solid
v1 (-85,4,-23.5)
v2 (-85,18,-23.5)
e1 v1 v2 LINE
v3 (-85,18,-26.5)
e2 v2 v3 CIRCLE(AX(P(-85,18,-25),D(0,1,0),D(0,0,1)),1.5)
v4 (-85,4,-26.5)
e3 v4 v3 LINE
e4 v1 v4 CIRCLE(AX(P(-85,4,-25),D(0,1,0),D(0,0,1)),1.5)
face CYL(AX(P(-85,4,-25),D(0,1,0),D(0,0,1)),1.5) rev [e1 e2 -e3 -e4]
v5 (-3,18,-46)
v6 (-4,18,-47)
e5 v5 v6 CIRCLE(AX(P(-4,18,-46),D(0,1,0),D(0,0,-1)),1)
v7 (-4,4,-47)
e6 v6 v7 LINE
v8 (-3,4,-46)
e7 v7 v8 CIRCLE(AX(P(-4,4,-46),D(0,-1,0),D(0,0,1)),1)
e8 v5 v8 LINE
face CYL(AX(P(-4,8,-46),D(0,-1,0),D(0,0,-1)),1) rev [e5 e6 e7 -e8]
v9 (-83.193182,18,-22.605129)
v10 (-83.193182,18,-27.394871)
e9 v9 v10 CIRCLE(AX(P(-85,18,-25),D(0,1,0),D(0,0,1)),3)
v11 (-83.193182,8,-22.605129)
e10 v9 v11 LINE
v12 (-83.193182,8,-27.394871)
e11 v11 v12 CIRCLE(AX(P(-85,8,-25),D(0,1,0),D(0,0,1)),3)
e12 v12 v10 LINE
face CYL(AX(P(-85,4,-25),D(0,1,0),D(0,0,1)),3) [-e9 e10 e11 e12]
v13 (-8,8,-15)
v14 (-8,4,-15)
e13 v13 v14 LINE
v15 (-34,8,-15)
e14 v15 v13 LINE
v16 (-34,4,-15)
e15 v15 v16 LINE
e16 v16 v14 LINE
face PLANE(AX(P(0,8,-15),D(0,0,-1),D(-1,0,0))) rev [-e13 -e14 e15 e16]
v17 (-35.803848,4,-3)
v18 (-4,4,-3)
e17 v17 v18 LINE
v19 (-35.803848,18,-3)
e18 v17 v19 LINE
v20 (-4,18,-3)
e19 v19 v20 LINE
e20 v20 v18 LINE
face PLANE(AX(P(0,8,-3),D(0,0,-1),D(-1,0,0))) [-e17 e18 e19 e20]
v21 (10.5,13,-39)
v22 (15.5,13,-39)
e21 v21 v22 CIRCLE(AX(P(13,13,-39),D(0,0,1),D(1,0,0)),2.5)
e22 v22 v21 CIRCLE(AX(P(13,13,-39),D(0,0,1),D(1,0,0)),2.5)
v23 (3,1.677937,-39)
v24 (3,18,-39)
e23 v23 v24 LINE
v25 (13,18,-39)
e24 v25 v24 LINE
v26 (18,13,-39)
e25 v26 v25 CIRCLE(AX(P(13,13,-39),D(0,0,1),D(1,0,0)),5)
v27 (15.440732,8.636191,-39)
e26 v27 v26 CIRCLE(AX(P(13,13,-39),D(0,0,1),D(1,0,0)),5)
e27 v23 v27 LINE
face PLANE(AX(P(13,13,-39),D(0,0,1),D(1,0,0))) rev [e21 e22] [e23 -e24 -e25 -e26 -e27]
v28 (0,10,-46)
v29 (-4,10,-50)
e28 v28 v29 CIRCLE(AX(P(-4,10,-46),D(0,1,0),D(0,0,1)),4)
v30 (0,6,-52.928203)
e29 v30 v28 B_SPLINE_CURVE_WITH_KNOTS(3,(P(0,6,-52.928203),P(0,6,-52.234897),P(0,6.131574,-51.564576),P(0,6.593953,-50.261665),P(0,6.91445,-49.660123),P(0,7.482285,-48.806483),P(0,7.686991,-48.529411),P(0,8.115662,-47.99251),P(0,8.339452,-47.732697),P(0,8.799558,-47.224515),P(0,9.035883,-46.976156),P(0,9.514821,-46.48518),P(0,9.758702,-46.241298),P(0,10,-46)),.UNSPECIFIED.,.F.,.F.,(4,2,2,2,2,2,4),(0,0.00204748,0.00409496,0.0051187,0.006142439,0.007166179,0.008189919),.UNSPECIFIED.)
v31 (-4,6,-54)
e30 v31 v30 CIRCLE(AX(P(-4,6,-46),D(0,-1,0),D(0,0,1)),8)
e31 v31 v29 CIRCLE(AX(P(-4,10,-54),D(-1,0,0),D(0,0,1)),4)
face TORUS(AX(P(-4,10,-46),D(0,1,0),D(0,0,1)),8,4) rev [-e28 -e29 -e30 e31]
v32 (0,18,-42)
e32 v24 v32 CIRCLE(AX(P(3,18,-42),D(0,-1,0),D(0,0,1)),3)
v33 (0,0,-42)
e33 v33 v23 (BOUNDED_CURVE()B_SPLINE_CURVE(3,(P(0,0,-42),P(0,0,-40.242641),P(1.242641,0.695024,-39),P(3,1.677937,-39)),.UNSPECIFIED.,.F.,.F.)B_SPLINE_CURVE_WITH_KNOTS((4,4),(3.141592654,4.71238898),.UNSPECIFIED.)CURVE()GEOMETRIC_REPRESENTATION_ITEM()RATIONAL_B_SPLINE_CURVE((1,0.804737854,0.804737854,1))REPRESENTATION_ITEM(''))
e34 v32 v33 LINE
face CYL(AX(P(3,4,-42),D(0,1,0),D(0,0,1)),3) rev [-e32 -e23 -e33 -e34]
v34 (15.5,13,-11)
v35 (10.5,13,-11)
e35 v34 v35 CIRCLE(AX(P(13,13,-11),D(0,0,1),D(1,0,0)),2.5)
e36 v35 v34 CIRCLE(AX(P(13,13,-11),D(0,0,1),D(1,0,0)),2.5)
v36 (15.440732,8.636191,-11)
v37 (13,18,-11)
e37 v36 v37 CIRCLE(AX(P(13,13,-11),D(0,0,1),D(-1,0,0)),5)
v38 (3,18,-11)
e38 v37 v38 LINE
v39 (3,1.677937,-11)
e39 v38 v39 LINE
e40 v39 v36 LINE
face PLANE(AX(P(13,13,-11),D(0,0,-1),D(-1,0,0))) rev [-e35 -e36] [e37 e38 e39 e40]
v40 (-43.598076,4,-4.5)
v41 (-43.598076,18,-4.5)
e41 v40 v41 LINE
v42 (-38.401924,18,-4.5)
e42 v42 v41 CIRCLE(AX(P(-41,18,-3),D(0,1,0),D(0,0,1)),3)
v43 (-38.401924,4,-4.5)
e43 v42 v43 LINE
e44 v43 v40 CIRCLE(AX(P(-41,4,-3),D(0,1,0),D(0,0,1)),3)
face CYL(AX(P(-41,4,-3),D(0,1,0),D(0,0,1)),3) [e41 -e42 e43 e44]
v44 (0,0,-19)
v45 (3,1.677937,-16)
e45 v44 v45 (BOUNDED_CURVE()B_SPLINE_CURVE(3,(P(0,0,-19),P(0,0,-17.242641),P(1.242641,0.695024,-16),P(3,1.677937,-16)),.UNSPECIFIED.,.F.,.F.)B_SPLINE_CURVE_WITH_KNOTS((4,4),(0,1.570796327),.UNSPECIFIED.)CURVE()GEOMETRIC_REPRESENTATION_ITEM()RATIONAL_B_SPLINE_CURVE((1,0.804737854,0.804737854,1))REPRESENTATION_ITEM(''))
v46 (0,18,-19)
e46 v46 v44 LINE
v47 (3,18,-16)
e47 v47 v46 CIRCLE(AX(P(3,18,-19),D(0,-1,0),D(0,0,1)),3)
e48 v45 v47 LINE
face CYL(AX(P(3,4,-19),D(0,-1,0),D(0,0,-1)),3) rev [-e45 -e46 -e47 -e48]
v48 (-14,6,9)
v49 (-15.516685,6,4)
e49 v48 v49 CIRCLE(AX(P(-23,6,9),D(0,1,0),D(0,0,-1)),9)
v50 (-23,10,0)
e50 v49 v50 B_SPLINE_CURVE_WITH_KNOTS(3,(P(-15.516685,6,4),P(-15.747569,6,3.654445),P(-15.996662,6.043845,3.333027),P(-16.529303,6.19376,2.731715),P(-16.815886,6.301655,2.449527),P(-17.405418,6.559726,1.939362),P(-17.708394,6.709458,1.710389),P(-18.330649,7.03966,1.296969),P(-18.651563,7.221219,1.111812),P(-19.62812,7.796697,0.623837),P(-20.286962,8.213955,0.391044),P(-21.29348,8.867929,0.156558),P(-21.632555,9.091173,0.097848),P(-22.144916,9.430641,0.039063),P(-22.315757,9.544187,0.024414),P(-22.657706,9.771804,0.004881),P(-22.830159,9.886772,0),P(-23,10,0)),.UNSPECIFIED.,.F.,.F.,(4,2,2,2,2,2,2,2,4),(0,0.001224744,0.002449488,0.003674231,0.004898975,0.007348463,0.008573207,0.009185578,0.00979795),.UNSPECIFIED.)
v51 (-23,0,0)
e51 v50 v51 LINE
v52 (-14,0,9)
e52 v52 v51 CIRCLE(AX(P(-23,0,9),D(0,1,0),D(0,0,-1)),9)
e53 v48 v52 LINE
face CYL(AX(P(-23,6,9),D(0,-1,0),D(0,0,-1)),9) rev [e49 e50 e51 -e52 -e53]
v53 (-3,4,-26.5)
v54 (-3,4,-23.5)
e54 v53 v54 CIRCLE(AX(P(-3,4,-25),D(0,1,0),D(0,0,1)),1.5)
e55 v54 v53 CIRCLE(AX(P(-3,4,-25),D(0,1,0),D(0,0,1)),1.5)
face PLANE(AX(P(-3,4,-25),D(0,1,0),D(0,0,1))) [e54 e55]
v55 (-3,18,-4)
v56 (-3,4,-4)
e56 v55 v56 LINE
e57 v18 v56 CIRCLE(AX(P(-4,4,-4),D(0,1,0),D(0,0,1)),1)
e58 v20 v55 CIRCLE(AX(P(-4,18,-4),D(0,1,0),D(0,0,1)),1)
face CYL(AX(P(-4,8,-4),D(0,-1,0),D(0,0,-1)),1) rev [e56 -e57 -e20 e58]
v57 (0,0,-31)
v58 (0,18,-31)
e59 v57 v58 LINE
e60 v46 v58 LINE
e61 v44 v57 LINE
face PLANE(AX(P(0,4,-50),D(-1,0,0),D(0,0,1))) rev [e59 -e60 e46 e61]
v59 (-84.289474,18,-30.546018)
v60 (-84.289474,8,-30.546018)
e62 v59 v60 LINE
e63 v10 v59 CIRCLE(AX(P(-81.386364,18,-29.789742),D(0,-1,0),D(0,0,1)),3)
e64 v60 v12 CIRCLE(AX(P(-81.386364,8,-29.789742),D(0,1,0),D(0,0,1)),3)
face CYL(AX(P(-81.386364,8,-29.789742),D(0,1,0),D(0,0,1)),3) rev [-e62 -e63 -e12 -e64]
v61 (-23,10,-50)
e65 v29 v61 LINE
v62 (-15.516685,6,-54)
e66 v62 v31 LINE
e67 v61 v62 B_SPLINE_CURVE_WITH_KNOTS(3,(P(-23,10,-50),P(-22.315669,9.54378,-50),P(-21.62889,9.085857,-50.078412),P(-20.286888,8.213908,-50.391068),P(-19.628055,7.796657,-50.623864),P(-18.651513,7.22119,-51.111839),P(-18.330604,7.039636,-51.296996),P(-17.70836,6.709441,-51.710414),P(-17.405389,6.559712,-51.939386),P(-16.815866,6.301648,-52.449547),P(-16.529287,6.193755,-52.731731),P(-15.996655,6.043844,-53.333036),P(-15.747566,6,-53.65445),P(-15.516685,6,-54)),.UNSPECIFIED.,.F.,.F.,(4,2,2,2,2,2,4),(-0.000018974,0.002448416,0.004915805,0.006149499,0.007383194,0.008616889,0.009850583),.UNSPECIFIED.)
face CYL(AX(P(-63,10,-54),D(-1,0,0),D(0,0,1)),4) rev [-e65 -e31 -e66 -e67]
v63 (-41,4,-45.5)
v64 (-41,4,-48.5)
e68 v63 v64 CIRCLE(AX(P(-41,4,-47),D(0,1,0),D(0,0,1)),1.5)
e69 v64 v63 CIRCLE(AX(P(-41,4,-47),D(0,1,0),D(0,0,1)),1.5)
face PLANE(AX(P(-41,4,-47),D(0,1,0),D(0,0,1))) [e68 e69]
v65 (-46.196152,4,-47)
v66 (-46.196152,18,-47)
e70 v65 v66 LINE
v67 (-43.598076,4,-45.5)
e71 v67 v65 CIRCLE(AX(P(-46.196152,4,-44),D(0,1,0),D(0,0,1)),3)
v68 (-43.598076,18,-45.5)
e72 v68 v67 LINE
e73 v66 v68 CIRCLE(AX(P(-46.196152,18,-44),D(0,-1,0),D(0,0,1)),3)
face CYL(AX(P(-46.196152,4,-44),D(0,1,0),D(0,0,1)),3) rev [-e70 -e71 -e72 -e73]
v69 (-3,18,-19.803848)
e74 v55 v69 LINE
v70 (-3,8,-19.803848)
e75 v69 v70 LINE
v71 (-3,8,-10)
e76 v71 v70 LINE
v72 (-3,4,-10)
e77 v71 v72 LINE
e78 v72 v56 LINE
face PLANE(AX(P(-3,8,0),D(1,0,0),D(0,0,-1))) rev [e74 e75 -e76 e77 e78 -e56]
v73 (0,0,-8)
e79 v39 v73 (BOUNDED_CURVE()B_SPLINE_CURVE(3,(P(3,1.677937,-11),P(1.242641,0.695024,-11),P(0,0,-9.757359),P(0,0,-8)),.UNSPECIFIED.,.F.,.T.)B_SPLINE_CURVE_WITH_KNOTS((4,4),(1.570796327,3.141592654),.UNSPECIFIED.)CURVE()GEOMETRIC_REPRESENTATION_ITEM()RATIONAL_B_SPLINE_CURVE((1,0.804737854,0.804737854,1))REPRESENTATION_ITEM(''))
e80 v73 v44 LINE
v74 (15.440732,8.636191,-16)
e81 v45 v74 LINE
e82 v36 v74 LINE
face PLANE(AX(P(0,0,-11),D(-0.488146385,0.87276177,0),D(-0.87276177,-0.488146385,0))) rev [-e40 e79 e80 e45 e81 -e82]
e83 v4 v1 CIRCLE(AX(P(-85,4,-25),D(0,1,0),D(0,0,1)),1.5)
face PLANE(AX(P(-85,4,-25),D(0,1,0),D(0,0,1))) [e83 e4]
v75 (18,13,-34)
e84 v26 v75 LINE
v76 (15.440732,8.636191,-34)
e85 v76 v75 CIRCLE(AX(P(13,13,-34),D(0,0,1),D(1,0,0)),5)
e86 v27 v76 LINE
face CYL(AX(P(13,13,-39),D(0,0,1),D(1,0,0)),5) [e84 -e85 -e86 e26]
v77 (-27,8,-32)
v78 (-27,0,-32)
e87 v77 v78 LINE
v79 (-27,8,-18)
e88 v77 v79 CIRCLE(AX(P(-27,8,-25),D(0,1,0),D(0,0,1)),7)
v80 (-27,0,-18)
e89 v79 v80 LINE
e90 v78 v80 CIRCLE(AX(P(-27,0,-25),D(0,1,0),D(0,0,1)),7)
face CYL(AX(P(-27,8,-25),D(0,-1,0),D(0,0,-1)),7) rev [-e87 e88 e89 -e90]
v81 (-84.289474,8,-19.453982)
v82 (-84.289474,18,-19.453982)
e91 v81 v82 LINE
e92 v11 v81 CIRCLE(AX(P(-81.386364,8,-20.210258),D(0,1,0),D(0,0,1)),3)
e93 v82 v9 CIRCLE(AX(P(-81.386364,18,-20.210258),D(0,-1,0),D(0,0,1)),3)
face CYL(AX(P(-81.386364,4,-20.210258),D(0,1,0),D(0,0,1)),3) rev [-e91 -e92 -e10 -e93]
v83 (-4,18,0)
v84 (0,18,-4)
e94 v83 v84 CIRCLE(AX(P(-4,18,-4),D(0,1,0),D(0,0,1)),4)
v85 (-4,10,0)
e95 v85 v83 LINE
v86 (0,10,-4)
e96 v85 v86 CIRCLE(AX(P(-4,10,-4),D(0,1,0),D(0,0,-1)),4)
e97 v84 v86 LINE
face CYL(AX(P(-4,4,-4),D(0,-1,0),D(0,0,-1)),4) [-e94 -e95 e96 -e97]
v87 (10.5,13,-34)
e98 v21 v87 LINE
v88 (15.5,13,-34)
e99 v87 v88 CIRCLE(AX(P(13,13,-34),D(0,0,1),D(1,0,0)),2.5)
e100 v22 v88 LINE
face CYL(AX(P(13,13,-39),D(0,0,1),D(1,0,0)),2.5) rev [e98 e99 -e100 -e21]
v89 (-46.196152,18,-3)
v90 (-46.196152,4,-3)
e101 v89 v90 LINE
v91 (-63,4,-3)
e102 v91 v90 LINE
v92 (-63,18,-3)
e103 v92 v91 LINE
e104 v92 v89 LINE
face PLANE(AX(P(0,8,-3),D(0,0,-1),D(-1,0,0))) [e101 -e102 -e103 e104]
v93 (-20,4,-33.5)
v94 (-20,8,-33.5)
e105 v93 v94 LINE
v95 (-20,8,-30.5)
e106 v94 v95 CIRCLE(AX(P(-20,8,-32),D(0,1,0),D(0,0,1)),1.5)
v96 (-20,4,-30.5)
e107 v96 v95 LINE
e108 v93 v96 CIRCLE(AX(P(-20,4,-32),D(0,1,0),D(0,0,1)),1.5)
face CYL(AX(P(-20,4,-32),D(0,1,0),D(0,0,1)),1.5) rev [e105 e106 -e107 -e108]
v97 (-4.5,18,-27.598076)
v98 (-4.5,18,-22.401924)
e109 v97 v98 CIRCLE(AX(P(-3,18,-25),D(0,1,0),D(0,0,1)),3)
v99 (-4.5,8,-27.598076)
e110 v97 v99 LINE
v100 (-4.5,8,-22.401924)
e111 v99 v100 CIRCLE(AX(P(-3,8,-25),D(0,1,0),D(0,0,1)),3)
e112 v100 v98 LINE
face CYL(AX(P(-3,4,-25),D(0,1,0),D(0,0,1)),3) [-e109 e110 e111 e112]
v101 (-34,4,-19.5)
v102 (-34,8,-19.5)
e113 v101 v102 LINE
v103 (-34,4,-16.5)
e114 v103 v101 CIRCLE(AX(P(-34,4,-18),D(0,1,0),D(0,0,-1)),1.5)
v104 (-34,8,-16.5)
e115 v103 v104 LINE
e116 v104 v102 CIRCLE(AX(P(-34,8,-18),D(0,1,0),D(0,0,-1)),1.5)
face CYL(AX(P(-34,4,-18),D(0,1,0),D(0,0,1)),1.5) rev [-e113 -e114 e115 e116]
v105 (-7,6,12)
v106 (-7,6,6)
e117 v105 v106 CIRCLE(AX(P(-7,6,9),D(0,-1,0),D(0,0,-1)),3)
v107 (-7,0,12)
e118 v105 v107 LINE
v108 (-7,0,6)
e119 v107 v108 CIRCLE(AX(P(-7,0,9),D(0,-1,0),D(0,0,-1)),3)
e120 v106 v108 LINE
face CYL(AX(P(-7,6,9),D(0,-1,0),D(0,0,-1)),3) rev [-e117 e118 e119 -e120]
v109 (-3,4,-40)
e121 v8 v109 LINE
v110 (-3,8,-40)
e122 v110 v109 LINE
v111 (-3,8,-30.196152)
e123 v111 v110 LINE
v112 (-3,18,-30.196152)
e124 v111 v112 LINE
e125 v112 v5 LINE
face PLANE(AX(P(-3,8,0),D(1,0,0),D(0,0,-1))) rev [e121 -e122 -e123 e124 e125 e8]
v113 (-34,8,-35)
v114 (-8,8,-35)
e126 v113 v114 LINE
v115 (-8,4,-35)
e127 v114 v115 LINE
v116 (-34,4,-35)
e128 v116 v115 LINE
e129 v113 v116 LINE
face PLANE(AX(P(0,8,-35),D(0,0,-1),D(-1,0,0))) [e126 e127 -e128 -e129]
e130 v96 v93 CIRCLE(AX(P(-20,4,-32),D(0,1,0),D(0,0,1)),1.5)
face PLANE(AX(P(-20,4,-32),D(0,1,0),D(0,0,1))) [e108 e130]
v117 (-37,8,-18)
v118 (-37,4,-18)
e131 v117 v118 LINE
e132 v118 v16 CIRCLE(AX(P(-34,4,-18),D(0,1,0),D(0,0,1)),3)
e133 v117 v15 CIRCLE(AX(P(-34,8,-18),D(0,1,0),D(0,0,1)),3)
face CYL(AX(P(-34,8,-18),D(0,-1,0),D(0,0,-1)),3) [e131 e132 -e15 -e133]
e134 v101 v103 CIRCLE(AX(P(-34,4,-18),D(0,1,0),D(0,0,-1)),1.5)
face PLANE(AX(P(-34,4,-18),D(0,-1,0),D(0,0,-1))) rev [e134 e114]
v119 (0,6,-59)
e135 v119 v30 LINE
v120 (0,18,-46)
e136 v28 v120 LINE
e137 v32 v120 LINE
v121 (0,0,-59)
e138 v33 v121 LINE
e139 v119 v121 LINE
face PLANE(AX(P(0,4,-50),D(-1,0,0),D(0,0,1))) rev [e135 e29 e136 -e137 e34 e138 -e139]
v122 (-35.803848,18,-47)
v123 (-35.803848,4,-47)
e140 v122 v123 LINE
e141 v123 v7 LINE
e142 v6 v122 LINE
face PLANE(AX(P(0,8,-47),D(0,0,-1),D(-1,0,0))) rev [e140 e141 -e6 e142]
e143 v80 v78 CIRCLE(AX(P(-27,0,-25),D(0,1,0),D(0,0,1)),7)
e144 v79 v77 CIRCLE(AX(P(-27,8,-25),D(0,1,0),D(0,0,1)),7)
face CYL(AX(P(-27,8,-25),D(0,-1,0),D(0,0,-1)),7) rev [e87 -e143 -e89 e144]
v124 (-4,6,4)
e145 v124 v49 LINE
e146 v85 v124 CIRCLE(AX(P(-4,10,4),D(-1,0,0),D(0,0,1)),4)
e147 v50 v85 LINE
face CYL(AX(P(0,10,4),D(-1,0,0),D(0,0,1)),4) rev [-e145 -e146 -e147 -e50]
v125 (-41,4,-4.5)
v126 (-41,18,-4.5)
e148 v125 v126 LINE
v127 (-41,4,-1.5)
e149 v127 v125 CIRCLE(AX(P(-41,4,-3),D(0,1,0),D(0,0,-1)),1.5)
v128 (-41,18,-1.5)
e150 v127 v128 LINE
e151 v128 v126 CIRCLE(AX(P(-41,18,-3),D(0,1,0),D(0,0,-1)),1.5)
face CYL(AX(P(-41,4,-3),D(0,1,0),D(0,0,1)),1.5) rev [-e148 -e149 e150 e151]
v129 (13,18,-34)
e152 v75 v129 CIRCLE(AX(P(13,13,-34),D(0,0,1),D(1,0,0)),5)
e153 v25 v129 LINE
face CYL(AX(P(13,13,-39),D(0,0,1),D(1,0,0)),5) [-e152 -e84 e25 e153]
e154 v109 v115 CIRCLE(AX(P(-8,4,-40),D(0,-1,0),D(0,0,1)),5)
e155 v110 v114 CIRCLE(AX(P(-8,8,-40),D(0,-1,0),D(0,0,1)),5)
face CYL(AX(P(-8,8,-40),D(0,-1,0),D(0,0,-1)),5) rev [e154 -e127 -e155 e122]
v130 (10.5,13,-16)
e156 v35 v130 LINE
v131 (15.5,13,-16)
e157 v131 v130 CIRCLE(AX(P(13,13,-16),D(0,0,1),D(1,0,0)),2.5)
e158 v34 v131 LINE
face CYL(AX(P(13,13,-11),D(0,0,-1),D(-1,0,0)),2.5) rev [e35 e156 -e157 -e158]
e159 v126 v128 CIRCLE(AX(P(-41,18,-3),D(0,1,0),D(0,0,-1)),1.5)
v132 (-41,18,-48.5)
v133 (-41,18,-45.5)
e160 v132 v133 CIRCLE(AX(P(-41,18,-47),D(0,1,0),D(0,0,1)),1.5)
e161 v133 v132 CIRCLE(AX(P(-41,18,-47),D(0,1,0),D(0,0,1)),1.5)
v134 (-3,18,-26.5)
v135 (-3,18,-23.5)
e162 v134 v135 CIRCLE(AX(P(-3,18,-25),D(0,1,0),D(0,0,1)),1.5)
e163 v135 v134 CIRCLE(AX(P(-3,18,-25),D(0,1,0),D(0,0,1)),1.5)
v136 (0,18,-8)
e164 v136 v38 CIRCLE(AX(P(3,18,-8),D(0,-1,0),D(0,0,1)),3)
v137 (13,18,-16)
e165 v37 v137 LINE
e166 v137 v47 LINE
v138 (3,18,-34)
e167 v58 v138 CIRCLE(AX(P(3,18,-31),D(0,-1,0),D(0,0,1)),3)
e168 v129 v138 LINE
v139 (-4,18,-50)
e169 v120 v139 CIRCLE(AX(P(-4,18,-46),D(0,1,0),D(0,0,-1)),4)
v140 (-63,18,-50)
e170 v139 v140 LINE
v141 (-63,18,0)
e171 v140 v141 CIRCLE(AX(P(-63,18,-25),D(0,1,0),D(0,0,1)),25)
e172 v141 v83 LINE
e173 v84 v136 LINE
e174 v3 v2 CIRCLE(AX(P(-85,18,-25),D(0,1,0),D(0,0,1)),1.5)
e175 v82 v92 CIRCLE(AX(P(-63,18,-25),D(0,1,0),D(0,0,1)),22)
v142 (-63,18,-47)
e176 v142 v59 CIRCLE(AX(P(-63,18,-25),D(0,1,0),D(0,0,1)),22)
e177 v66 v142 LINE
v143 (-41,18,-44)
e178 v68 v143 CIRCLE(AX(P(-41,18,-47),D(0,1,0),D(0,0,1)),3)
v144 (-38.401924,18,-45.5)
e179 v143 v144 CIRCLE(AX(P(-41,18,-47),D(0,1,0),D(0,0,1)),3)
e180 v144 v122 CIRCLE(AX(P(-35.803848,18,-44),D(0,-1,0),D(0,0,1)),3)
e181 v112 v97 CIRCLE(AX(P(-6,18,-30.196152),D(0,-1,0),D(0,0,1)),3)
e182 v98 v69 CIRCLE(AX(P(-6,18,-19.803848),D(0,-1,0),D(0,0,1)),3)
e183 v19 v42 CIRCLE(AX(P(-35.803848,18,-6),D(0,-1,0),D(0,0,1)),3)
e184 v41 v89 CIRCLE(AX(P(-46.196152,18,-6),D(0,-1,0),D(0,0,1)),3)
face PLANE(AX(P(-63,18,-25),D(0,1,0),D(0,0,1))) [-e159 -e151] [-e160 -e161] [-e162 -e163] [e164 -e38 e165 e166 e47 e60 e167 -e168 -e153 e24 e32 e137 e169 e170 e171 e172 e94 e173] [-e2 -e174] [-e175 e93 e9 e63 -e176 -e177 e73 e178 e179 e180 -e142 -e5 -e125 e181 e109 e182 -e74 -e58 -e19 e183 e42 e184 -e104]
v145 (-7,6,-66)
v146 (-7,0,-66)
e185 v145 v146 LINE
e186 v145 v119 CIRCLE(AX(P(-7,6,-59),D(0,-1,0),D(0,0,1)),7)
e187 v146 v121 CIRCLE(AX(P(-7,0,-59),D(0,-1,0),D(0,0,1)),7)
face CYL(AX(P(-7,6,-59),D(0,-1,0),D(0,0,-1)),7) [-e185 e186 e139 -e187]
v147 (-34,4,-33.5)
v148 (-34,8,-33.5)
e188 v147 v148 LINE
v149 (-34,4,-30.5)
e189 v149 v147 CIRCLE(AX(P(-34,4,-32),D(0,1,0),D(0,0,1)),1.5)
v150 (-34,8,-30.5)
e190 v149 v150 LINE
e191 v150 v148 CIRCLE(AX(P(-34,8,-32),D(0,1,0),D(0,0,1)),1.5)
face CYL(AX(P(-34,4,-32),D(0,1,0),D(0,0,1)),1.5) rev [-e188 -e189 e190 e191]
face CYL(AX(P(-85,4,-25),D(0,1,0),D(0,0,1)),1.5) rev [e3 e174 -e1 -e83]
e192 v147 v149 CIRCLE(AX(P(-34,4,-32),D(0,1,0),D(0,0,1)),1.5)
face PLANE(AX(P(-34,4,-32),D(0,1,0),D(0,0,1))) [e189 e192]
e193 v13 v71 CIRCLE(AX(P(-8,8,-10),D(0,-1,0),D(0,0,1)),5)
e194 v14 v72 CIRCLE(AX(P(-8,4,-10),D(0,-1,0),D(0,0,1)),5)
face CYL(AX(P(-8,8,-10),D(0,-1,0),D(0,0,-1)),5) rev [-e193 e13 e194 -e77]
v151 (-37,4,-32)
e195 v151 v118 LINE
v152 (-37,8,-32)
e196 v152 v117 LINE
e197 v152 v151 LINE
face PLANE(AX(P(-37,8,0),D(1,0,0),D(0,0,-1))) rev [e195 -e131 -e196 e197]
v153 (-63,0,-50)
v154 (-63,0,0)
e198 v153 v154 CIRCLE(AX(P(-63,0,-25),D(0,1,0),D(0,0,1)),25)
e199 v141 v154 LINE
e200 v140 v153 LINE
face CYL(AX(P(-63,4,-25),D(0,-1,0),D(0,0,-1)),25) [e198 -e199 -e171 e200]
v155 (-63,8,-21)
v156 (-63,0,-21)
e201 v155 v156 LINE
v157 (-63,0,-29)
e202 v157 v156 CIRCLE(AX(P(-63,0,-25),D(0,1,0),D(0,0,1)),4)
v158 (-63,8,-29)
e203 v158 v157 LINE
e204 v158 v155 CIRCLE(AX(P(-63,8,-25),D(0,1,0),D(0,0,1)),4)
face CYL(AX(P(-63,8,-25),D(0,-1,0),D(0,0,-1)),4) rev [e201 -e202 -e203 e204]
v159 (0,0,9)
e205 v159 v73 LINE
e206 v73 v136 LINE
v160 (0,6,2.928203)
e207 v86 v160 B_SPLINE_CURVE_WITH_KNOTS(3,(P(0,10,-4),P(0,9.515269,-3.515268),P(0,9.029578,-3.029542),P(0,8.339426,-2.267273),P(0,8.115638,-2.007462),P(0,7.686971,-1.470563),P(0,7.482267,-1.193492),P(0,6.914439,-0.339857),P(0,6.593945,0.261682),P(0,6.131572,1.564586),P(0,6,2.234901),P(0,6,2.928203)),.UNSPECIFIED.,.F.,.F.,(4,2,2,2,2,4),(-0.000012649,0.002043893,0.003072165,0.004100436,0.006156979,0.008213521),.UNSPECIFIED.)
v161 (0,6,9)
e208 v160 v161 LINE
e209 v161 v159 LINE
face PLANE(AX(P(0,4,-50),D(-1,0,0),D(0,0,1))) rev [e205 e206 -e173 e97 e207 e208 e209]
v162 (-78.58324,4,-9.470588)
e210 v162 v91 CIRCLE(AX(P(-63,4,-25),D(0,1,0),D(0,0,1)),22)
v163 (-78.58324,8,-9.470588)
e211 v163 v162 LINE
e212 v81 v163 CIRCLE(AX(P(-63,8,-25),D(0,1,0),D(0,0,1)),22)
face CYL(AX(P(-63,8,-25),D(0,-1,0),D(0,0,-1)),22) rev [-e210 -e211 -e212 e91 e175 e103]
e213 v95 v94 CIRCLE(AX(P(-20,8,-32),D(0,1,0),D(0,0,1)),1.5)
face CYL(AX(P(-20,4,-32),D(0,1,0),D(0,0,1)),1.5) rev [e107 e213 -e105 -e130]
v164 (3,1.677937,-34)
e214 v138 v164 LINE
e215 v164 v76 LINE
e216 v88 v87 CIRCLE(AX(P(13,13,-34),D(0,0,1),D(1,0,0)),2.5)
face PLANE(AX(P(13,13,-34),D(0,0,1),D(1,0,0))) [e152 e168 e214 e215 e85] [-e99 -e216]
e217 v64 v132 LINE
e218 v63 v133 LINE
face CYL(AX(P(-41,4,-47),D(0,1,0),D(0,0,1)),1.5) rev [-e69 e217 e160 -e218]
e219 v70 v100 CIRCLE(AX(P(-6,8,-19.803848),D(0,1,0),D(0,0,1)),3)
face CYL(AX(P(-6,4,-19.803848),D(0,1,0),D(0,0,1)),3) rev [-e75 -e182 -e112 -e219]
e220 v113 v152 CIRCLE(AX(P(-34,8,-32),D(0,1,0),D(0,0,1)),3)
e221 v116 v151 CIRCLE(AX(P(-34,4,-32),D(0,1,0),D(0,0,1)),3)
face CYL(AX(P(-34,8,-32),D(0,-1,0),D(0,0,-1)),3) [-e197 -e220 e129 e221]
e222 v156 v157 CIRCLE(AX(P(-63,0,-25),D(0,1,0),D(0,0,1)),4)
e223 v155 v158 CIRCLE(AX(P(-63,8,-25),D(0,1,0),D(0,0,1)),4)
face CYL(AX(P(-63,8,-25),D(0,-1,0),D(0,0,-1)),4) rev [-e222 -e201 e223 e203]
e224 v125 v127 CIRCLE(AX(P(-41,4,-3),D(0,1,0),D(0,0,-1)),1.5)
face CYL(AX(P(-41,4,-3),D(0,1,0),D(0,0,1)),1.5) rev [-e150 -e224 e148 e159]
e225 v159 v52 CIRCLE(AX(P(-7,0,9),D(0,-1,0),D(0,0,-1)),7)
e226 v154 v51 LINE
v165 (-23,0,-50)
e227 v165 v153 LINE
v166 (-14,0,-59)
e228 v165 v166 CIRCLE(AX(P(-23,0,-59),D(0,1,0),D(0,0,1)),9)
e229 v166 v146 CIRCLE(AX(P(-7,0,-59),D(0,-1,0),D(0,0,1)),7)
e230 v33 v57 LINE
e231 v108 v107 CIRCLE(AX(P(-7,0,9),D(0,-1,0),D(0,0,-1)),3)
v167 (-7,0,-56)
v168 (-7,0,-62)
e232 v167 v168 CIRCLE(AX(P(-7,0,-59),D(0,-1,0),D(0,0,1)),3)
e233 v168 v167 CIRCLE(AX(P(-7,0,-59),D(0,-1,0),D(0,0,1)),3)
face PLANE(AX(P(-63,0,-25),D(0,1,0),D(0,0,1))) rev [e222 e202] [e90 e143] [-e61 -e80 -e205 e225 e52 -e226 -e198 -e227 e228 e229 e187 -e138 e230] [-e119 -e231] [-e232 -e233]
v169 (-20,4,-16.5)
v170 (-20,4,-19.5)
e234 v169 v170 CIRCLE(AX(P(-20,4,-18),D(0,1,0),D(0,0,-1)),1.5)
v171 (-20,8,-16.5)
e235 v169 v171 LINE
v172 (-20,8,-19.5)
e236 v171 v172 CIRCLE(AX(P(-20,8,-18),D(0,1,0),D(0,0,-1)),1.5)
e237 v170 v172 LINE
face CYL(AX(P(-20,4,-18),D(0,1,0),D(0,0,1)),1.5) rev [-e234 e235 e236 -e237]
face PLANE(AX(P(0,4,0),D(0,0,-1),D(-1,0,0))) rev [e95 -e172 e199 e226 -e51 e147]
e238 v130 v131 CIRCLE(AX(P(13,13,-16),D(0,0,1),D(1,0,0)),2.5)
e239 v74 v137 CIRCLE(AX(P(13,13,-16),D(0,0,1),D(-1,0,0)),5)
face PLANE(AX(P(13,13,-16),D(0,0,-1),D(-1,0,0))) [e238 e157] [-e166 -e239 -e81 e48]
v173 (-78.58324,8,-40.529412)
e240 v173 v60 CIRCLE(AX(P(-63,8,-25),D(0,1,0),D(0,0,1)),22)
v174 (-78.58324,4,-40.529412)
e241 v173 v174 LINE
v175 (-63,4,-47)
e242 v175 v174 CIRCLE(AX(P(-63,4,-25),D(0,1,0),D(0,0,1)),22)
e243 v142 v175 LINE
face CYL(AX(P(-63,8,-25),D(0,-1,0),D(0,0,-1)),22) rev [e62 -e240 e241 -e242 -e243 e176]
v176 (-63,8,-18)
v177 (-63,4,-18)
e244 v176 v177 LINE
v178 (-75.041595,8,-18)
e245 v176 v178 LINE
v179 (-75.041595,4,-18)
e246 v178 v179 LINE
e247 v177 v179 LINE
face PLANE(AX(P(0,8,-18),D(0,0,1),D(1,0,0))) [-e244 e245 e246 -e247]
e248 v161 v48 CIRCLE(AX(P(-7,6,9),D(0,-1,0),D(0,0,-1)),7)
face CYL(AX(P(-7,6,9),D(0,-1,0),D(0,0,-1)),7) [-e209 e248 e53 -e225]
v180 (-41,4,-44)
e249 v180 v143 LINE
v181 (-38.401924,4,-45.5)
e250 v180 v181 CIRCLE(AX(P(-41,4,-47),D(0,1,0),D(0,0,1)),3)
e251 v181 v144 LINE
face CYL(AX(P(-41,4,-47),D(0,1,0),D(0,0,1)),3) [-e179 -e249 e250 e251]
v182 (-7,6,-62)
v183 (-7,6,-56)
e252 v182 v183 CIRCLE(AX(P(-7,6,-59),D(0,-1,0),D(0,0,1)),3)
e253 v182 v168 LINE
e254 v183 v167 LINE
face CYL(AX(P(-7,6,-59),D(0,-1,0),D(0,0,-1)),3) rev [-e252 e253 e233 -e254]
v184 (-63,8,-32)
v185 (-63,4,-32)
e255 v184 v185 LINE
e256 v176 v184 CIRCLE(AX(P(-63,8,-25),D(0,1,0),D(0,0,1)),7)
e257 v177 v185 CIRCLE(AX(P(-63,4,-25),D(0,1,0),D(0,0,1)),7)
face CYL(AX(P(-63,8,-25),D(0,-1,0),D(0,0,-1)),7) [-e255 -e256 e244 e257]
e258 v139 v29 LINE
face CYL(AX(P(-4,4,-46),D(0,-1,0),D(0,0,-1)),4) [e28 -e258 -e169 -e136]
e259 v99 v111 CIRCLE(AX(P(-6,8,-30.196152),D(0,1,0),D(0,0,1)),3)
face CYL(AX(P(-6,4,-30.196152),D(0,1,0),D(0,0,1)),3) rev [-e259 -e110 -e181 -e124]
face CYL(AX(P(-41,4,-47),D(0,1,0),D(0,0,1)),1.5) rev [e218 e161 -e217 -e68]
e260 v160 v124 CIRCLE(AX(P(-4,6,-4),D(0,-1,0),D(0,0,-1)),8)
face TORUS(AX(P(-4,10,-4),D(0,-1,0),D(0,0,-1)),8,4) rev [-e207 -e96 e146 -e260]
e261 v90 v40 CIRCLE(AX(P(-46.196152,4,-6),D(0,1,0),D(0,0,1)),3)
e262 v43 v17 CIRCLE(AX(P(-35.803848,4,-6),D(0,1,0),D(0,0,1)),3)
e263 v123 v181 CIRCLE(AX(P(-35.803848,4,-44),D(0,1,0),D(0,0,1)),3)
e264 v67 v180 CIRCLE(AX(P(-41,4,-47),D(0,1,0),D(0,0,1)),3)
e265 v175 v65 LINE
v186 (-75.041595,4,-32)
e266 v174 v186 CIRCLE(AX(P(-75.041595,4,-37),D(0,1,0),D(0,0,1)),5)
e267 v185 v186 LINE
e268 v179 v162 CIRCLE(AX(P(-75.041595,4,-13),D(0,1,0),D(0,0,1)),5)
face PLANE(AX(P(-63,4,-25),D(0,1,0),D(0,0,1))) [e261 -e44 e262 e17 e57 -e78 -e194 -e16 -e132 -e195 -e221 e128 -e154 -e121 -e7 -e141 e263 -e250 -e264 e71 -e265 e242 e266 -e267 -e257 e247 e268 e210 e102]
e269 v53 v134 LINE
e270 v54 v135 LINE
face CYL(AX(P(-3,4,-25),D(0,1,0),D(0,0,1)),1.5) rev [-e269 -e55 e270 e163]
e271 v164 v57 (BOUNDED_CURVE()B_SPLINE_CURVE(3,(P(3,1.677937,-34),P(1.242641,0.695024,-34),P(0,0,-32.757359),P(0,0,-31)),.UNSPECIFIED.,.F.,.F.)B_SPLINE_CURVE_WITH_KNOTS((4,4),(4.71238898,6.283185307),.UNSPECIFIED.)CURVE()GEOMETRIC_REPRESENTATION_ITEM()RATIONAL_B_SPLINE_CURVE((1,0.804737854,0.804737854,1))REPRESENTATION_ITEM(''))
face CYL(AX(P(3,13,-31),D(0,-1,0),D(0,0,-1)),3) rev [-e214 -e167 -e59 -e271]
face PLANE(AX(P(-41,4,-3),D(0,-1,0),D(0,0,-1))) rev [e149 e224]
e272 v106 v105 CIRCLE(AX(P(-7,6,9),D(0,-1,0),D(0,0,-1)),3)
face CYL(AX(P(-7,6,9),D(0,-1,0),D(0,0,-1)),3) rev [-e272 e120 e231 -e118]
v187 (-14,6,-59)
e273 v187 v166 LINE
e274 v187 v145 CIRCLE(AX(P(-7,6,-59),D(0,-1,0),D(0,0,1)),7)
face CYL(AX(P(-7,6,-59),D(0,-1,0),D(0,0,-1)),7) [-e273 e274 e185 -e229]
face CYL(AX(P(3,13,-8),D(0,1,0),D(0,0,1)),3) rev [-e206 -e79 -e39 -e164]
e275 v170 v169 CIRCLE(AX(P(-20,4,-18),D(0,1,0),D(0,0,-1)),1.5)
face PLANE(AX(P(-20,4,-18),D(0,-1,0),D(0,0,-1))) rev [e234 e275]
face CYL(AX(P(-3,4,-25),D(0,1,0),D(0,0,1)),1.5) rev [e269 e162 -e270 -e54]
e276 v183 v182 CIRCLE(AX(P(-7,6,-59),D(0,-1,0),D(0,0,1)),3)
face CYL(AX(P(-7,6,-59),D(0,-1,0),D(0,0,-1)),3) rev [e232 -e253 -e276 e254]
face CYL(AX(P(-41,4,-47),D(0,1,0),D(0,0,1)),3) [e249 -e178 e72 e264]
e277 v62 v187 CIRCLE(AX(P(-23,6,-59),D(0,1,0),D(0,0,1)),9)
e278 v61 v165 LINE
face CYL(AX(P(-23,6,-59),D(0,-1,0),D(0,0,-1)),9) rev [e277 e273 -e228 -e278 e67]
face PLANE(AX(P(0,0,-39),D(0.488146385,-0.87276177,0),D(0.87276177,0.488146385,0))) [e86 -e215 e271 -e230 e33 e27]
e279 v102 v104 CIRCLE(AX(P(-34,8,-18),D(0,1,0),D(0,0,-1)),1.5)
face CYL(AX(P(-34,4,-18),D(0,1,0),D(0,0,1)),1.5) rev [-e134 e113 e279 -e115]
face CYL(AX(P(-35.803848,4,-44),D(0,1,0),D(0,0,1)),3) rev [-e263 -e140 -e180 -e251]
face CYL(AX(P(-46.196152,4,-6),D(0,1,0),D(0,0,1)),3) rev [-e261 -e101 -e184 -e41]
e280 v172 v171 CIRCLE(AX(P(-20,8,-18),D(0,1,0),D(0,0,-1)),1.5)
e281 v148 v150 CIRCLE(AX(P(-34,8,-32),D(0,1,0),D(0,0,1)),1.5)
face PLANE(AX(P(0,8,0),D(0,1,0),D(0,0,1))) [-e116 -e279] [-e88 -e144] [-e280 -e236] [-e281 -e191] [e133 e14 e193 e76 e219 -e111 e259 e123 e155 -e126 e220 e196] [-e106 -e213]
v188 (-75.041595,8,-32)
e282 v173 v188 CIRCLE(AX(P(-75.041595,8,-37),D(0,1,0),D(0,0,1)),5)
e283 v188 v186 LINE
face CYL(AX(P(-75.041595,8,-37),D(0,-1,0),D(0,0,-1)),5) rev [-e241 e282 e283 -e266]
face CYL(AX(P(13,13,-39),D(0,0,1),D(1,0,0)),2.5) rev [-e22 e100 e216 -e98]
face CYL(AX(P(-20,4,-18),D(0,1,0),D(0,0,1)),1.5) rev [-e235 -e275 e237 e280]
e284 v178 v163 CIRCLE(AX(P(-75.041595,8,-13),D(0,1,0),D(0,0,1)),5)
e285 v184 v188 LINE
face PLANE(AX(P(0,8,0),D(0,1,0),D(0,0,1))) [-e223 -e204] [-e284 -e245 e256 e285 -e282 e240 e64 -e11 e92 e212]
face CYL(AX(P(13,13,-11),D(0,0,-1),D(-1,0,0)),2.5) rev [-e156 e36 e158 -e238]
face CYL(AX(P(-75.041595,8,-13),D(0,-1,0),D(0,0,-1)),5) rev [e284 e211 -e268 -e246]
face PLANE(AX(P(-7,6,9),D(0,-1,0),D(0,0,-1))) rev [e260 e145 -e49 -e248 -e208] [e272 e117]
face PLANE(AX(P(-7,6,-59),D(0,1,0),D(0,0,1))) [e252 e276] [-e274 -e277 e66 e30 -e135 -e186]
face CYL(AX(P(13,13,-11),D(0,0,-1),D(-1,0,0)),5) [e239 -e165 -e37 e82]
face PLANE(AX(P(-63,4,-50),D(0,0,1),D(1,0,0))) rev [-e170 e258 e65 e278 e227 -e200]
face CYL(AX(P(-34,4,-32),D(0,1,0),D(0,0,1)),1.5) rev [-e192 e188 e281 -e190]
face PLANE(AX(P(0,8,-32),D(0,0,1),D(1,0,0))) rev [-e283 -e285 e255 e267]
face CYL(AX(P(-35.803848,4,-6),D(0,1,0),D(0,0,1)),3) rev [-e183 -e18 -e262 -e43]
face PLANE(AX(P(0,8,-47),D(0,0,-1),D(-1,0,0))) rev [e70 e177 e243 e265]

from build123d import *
from build123d.topology import SkipClean

# Parameters (mm, degrees)
BASE_PLATE_4MM_DEPTH       = 4
BASE_PLATE_FILLET_R4_R     = 4
HOUSING_START              = 4
HOUSING_WALL_SKETCH_R      = 7
HOUSING_WALL_SKETCH_R_2    = 4
HOUSING_WALLS_DEPTH        = 4
WALL_START                 = 10
WALL_RIM_10MM_DEPTH        = 10
BEARING_BOSS_14MM_DEPTH    = 14
BOSS_POCKET_SKETCH_R       = 1.5
BOSS_POCKET_CUT_DEPTH      = 14
WALL_SLOT_SKETCH_R         = 4
WALL_SLOT_SKETCH_R_2       = 7
WALL_SLOT_CUT_DEPTH        = 14
BEARING_BOSS_FILLET_R3_A_R = 3
BEARING_BOSS_FILLET_R3_B_R = 3
WALL_NOTCH_SKETCH_R        = 1.5
WALL_NOTCH_CUT_DEPTH       = 4
MOUNTING_START             = -6
MOUNTING_EAR_SKETCH_R      = 3
MOUNTING_EARS_6MM_DEPTH    = 6
SIDE_LUG_SKETCH_R          = 2.5
SIDE_LUG_5MM_DEPTH         = 5
SIDE_LUG_FILLET_R3_R       = 3
CLEVIS_START               = 5
CLEVIS_LUG_SKETCH_R        = 2.5
CLEVIS_LUG_5MM_DEPTH       = 5
CLEVIS_LUG_FILLET_R3_R     = 3
MOUNTING_EAR_FILLET_R4_A_R = 4
MOUNTING_EAR_FILLET_R4_B_R = 4


with BuildPart() as part:
    # Base Plate Sketch → Base Plate 4mm (new body)
    with BuildSketch(Plane(origin=(0, 0, 0), x_dir=(1, 0, 0), z_dir=(0, 1, 0))):
        with BuildLine():
            Line((0, 0), (-63, 0))
            ThreePointArc((-63, 0), (-88, 25), (-63, 50))
            Line((-63, 50), (0, 50))
            Line((0, 50), (0, 0))
        make_face()
    extrude(amount=BASE_PLATE_4MM_DEPTH)

    # Base Plate Fillet R4
    base_plate_fillet_r4_edges = [part.edges().sort_by_distance(p)[0] for p in [
        (0, 2, 0),
        (0, 2, -50),
    ]]
    fillet(base_plate_fillet_r4_edges, radius=BASE_PLATE_FILLET_R4_R)

    # Housing Wall Sketch → Housing Walls (add)
    # profile 1 of 4: a face of its own
    with BuildSketch(Plane(origin=(0, 4, 0), x_dir=(1, 0, 0), z_dir=(0, 1, 0)).offset(HOUSING_START)):
        with BuildLine():
            ThreePointArc((-4, 0), (-1.171572875, 1.171572875), (0, 4))
            Line((0, 4), (0, 46))
            ThreePointArc((0, 46), (-1.171572875, 48.828427125), (-4, 50))
            Line((-4, 50), (-63, 50))
            ThreePointArc((-63, 50), (-88, 25), (-63, 0))
            Line((-63, 0), (-4, 0))
        make_face()
        with BuildLine():
            Line((-63, 47), (-4, 47))
            ThreePointArc((-4, 47), (-3.292893219, 46.707106781), (-3, 46))
            Line((-3, 46), (-3, 4))
            ThreePointArc((-3, 4), (-3.292893219, 3.292893219), (-4, 3))
            Line((-4, 3), (-63, 3))
            ThreePointArc((-63, 3), (-85, 25), (-63, 47))
        make_face(mode=Mode.SUBTRACT)
    # profile 2 of 4: a face of its own
    with BuildSketch(Plane(origin=(0, 4, 0), x_dir=(1, 0, 0), z_dir=(0, 1, 0)).offset(HOUSING_START)):
        with BuildLine():
            ThreePointArc((-8, 15), (-4.464466094, 13.535533906), (-3, 10))
            Line((-3, 10), (-3, 40))
            ThreePointArc((-3, 40), (-4.464466094, 36.464466094), (-8, 35))
            Line((-8, 35), (-34, 35))
            ThreePointArc((-34, 35), (-36.121320344, 34.121320344), (-37, 32))
            Line((-37, 32), (-37, 18))
            ThreePointArc((-37, 18), (-36.121320344, 15.878679656), (-34, 15))
            Line((-34, 15), (-8, 15))
        make_face()
        with Locations(Location((-27, 25, 0), (0, 0, 270))):
            Circle(HOUSING_WALL_SKETCH_R, mode=Mode.SUBTRACT)
    # profile 3 of 4: a face of its own
    with BuildSketch(Plane(origin=(0, 4, 0), x_dir=(1, 0, 0), z_dir=(0, 1, 0)).offset(HOUSING_START)):
        with Locations((-63, 25)):
            Circle(HOUSING_WALL_SKETCH_R)
        with Locations(Location((-63, 25, 0), (0, 0, 270))):
            Circle(HOUSING_WALL_SKETCH_R_2, mode=Mode.SUBTRACT)
    # profile 4 of 4: a face of its own
    with BuildSketch(Plane(origin=(0, 4, 0), x_dir=(1, 0, 0), z_dir=(0, 1, 0)).offset(HOUSING_START)):
        with BuildLine():
            ThreePointArc((-78.583240043, 40.529411765), (-85, 25), (-78.583240043, 9.470588235))
            ThreePointArc((-78.583240043, 9.470588235), (-79.659335305, 14.917412472), (-75.041594579, 18))
            Line((-75.041594579, 18), (-63, 18))
            ThreePointArc((-63, 18), (-70, 25), (-63, 32))
            Line((-63, 32), (-75.041594579, 32))
            ThreePointArc((-75.041594579, 32), (-79.659335305, 35.082587528), (-78.583240043, 40.529411765))
        make_face()
    extrude(amount=-HOUSING_WALLS_DEPTH)

    # Wall Rim Sketch → Wall Rim 10mm (add)
    with SkipClean():  # the faces are left unmerged after this step: merging them gives an invalid solid
        with BuildSketch(Plane(origin=(0, 8, 0), x_dir=(1, 0, 0), z_dir=(0, 1, 0)).offset(WALL_START)):
            with BuildLine():
                Line((-63, 50), (-4, 50))
                ThreePointArc((-4, 50), (-1.171572875, 48.828427125), (0, 46))
                Line((0, 46), (0, 4))
                ThreePointArc((0, 4), (-1.171572875, 1.171572875), (-4, 0))
                Line((-4, 0), (-63, 0))
                ThreePointArc((-63, 0), (-88, 25), (-63, 50))
            make_face()
            with BuildLine():
                Line((-63, 3), (-4, 3))
                ThreePointArc((-4, 3), (-3.292893219, 3.292893219), (-3, 4))
                Line((-3, 4), (-3, 46))
                ThreePointArc((-3, 46), (-3.292893219, 46.707106781), (-4, 47))
                Line((-4, 47), (-63, 47))
                ThreePointArc((-63, 47), (-85, 25), (-63, 3))
            make_face(mode=Mode.SUBTRACT)
        extrude(amount=-WALL_RIM_10MM_DEPTH)

    # Bearing Boss Sketch → Bearing Boss 14mm (add)
    with BuildSketch(Plane(origin=(0, 18, 0), x_dir=(1, 0, 0), z_dir=(0, 1, 0))):
        with BuildLine():
            ThreePointArc((-84.795454545, 22.006981264), (-82, 25), (-84.795454545, 27.993018736))
            ThreePointArc((-84.795454545, 27.993018736), (-85, 25), (-84.795454545, 22.006981264))
        make_face()
        with BuildLine():
            ThreePointArc((-38, 3), (-41, 6), (-44, 3))
            Line((-44, 3), (-38, 3))
        make_face()
        with BuildLine():
            Line((-3, 22), (-3, 28))
            ThreePointArc((-3, 28), (-6, 25), (-3, 22))
        make_face()
        with BuildLine():
            Line((-38, 47), (-44, 47))
            ThreePointArc((-44, 47), (-41, 44), (-38, 47))
        make_face()
    extrude(amount=-BEARING_BOSS_14MM_DEPTH)

    # Boss Pocket Sketch → Boss Pocket Cut (cut)
    with BuildSketch(Plane(origin=(0, 18, 0), x_dir=(1, 0, 0), z_dir=(0, 1, 0))):
        with Locations(Location((-85, 25, 0), (0, 0, 270))):
            Circle(BOSS_POCKET_SKETCH_R)
        with Locations(Location((-41, 3, 0), (0, 0, 90))):
            Circle(BOSS_POCKET_SKETCH_R)
        with Locations(Location((-41, 47, 0), (0, 0, 270))):
            Circle(BOSS_POCKET_SKETCH_R)
        with Locations(Location((-3, 25, 0), (0, 0, 270))):
            Circle(BOSS_POCKET_SKETCH_R)
    extrude(amount=-BOSS_POCKET_CUT_DEPTH, mode=Mode.SUBTRACT)

    # Wall Slot Sketch → Wall Slot Cut (cut)
    with BuildSketch(Plane(origin=(0, 4, 0), x_dir=(1, 0, 0), z_dir=(0, 1, 0))):
        with Locations(Location((-63, 25, 0), (0, 0, 270))):
            Circle(WALL_SLOT_SKETCH_R)
        with Locations(Location((-27, 25, 0), (0, 0, 270))):
            Circle(WALL_SLOT_SKETCH_R_2)
    extrude(amount=-WALL_SLOT_CUT_DEPTH, mode=Mode.SUBTRACT)

    # Bearing Boss Fillet R3 A
    bearing_boss_fillet_r3_a_edges = [part.edges().sort_by_distance(p)[0] for p in [
        (-84.795454545, 13, -22.006981264),
        (-84.795454545, 13, -27.993018736),
    ]]
    fillet(bearing_boss_fillet_r3_a_edges, radius=BEARING_BOSS_FILLET_R3_A_R)

    # Bearing Boss Fillet R3 B
    bearing_boss_fillet_r3_b_edges = [part.edges().sort_by_distance(p)[0] for p in [
        (-38, 11, -3),
        (-44, 11, -3),
        (-3, 13, -28),
        (-3, 13, -22),
        (-44, 11, -47),
        (-38, 11, -47),
    ]]
    fillet(bearing_boss_fillet_r3_b_edges, radius=BEARING_BOSS_FILLET_R3_B_R)

    # Wall Notch Sketch → Wall Notch Cut (cut)
    with BuildSketch(Plane(origin=(0, 8, 0), x_dir=(1, 0, 0), z_dir=(0, 1, 0))):
        with Locations(Location((-34, 32, 0), (0, 0, 270))):
            Circle(WALL_NOTCH_SKETCH_R)
        with Locations(Location((-20, 32, 0), (0, 0, 270))):
            Circle(WALL_NOTCH_SKETCH_R)
        with Locations(Location((-20, 18, 0), (0, 0, 90))):
            Circle(WALL_NOTCH_SKETCH_R)
        with Locations(Location((-34, 18, 0), (0, 0, 90))):
            Circle(WALL_NOTCH_SKETCH_R)
    extrude(amount=-WALL_NOTCH_CUT_DEPTH, mode=Mode.SUBTRACT)

    # Mounting Ear Sketch → Mounting Ears 6mm (add)
    # profile 1 of 2: a face of its own
    with BuildSketch(Plane.XZ.offset(MOUNTING_START)):
        with BuildLine():
            Line((0, 9), (0, -4))
            ThreePointArc((0, -4), (-1.171572875, -1.171572875), (-4, 0))
            Line((-4, 0), (-23, 0))
            ThreePointArc((-23, 0), (-16.636038969, 2.636038969), (-14, 9))
            ThreePointArc((-14, 9), (-7, 16), (0, 9))
        make_face()
        with Locations(Location((-7, 9, 0), (0, 0, 270))):
            Circle(MOUNTING_EAR_SKETCH_R, mode=Mode.SUBTRACT)
    # profile 2 of 2: a face of its own
    with BuildSketch(Plane.XZ.offset(MOUNTING_START)):
        with BuildLine():
            Line((-23, -50), (-4, -50))
            ThreePointArc((-4, -50), (-1.171572875, -48.828427125), (0, -46))
            Line((0, -46), (0, -59))
            ThreePointArc((0, -59), (-7, -66), (-14, -59))
            ThreePointArc((-14, -59), (-16.636038969, -52.636038969), (-23, -50))
        make_face()
        with Locations(Location((-7, -59, 0), (0, 0, 90))):
            Circle(MOUNTING_EAR_SKETCH_R, mode=Mode.SUBTRACT)
    extrude(amount=MOUNTING_EARS_6MM_DEPTH)

    # Side Lug Sketch → Side Lug 5mm (add)
    with BuildSketch(Plane.XY.offset(-34)):
        with BuildLine():
            Line((0, 18), (13, 18))
            ThreePointArc((13, 18), (17.838338777, 14.261141498), (15.440731926, 8.636191151))
            Line((15.440731926, 8.636191151), (0, 0))
            Line((0, 0), (0, 18))
        make_face()
        with Locations((13, 13)):
            Circle(SIDE_LUG_SKETCH_R, mode=Mode.SUBTRACT)
    extrude(amount=-SIDE_LUG_5MM_DEPTH)

    # Side Lug Fillet R3
    side_lug_fillet_r3_edges = [part.edges().sort_by_distance(p)[0] for p in [
        (0, 9, -39),
        (0, 9, -34),
    ]]
    fillet(side_lug_fillet_r3_edges, radius=SIDE_LUG_FILLET_R3_R)

    # Clevis Lug Sketch → Clevis Lug 5mm (add)
    with BuildSketch(Plane.XY.offset(-16).offset(CLEVIS_START)):
        with BuildLine():
            Line((0, 18), (0, 0))
            Line((0, 0), (15.440731926, 8.636191151))
            ThreePointArc((15.440731926, 8.636191151), (17.838338777, 14.261141498), (13, 18))
            Line((13, 18), (0, 18))
        make_face()
        with Locations((13, 13)):
            Circle(CLEVIS_LUG_SKETCH_R, mode=Mode.SUBTRACT)
    extrude(amount=-CLEVIS_LUG_5MM_DEPTH)

    # Clevis Lug Fillet R3
    clevis_lug_fillet_r3_edges = [part.edges().sort_by_distance(p)[0] for p in [
        (0, 9, -11),
        (0, 9, -16),
    ]]
    fillet(clevis_lug_fillet_r3_edges, radius=CLEVIS_LUG_FILLET_R3_R)

    # Mounting Ear Fillet R4 A
    mounting_ear_fillet_r4_a_edges = [part.edges().sort_by_distance(p)[0] for p in [
        (-1.171572875, 6, -1.171572875),
        (-13.5, 6, 0),
    ]]
    fillet(mounting_ear_fillet_r4_a_edges, radius=MOUNTING_EAR_FILLET_R4_A_R)

    # Mounting Ear Fillet R4 B
    mounting_ear_fillet_r4_b_edges = [part.edges().sort_by_distance(p)[0] for p in [
        (-13.5, 6, -50),
        (-1.171572875, 6, -48.828427125),
    ]]
    fillet(mounting_ear_fillet_r4_b_edges, radius=MOUNTING_EAR_FILLET_R4_B_R)


solid = part.part
